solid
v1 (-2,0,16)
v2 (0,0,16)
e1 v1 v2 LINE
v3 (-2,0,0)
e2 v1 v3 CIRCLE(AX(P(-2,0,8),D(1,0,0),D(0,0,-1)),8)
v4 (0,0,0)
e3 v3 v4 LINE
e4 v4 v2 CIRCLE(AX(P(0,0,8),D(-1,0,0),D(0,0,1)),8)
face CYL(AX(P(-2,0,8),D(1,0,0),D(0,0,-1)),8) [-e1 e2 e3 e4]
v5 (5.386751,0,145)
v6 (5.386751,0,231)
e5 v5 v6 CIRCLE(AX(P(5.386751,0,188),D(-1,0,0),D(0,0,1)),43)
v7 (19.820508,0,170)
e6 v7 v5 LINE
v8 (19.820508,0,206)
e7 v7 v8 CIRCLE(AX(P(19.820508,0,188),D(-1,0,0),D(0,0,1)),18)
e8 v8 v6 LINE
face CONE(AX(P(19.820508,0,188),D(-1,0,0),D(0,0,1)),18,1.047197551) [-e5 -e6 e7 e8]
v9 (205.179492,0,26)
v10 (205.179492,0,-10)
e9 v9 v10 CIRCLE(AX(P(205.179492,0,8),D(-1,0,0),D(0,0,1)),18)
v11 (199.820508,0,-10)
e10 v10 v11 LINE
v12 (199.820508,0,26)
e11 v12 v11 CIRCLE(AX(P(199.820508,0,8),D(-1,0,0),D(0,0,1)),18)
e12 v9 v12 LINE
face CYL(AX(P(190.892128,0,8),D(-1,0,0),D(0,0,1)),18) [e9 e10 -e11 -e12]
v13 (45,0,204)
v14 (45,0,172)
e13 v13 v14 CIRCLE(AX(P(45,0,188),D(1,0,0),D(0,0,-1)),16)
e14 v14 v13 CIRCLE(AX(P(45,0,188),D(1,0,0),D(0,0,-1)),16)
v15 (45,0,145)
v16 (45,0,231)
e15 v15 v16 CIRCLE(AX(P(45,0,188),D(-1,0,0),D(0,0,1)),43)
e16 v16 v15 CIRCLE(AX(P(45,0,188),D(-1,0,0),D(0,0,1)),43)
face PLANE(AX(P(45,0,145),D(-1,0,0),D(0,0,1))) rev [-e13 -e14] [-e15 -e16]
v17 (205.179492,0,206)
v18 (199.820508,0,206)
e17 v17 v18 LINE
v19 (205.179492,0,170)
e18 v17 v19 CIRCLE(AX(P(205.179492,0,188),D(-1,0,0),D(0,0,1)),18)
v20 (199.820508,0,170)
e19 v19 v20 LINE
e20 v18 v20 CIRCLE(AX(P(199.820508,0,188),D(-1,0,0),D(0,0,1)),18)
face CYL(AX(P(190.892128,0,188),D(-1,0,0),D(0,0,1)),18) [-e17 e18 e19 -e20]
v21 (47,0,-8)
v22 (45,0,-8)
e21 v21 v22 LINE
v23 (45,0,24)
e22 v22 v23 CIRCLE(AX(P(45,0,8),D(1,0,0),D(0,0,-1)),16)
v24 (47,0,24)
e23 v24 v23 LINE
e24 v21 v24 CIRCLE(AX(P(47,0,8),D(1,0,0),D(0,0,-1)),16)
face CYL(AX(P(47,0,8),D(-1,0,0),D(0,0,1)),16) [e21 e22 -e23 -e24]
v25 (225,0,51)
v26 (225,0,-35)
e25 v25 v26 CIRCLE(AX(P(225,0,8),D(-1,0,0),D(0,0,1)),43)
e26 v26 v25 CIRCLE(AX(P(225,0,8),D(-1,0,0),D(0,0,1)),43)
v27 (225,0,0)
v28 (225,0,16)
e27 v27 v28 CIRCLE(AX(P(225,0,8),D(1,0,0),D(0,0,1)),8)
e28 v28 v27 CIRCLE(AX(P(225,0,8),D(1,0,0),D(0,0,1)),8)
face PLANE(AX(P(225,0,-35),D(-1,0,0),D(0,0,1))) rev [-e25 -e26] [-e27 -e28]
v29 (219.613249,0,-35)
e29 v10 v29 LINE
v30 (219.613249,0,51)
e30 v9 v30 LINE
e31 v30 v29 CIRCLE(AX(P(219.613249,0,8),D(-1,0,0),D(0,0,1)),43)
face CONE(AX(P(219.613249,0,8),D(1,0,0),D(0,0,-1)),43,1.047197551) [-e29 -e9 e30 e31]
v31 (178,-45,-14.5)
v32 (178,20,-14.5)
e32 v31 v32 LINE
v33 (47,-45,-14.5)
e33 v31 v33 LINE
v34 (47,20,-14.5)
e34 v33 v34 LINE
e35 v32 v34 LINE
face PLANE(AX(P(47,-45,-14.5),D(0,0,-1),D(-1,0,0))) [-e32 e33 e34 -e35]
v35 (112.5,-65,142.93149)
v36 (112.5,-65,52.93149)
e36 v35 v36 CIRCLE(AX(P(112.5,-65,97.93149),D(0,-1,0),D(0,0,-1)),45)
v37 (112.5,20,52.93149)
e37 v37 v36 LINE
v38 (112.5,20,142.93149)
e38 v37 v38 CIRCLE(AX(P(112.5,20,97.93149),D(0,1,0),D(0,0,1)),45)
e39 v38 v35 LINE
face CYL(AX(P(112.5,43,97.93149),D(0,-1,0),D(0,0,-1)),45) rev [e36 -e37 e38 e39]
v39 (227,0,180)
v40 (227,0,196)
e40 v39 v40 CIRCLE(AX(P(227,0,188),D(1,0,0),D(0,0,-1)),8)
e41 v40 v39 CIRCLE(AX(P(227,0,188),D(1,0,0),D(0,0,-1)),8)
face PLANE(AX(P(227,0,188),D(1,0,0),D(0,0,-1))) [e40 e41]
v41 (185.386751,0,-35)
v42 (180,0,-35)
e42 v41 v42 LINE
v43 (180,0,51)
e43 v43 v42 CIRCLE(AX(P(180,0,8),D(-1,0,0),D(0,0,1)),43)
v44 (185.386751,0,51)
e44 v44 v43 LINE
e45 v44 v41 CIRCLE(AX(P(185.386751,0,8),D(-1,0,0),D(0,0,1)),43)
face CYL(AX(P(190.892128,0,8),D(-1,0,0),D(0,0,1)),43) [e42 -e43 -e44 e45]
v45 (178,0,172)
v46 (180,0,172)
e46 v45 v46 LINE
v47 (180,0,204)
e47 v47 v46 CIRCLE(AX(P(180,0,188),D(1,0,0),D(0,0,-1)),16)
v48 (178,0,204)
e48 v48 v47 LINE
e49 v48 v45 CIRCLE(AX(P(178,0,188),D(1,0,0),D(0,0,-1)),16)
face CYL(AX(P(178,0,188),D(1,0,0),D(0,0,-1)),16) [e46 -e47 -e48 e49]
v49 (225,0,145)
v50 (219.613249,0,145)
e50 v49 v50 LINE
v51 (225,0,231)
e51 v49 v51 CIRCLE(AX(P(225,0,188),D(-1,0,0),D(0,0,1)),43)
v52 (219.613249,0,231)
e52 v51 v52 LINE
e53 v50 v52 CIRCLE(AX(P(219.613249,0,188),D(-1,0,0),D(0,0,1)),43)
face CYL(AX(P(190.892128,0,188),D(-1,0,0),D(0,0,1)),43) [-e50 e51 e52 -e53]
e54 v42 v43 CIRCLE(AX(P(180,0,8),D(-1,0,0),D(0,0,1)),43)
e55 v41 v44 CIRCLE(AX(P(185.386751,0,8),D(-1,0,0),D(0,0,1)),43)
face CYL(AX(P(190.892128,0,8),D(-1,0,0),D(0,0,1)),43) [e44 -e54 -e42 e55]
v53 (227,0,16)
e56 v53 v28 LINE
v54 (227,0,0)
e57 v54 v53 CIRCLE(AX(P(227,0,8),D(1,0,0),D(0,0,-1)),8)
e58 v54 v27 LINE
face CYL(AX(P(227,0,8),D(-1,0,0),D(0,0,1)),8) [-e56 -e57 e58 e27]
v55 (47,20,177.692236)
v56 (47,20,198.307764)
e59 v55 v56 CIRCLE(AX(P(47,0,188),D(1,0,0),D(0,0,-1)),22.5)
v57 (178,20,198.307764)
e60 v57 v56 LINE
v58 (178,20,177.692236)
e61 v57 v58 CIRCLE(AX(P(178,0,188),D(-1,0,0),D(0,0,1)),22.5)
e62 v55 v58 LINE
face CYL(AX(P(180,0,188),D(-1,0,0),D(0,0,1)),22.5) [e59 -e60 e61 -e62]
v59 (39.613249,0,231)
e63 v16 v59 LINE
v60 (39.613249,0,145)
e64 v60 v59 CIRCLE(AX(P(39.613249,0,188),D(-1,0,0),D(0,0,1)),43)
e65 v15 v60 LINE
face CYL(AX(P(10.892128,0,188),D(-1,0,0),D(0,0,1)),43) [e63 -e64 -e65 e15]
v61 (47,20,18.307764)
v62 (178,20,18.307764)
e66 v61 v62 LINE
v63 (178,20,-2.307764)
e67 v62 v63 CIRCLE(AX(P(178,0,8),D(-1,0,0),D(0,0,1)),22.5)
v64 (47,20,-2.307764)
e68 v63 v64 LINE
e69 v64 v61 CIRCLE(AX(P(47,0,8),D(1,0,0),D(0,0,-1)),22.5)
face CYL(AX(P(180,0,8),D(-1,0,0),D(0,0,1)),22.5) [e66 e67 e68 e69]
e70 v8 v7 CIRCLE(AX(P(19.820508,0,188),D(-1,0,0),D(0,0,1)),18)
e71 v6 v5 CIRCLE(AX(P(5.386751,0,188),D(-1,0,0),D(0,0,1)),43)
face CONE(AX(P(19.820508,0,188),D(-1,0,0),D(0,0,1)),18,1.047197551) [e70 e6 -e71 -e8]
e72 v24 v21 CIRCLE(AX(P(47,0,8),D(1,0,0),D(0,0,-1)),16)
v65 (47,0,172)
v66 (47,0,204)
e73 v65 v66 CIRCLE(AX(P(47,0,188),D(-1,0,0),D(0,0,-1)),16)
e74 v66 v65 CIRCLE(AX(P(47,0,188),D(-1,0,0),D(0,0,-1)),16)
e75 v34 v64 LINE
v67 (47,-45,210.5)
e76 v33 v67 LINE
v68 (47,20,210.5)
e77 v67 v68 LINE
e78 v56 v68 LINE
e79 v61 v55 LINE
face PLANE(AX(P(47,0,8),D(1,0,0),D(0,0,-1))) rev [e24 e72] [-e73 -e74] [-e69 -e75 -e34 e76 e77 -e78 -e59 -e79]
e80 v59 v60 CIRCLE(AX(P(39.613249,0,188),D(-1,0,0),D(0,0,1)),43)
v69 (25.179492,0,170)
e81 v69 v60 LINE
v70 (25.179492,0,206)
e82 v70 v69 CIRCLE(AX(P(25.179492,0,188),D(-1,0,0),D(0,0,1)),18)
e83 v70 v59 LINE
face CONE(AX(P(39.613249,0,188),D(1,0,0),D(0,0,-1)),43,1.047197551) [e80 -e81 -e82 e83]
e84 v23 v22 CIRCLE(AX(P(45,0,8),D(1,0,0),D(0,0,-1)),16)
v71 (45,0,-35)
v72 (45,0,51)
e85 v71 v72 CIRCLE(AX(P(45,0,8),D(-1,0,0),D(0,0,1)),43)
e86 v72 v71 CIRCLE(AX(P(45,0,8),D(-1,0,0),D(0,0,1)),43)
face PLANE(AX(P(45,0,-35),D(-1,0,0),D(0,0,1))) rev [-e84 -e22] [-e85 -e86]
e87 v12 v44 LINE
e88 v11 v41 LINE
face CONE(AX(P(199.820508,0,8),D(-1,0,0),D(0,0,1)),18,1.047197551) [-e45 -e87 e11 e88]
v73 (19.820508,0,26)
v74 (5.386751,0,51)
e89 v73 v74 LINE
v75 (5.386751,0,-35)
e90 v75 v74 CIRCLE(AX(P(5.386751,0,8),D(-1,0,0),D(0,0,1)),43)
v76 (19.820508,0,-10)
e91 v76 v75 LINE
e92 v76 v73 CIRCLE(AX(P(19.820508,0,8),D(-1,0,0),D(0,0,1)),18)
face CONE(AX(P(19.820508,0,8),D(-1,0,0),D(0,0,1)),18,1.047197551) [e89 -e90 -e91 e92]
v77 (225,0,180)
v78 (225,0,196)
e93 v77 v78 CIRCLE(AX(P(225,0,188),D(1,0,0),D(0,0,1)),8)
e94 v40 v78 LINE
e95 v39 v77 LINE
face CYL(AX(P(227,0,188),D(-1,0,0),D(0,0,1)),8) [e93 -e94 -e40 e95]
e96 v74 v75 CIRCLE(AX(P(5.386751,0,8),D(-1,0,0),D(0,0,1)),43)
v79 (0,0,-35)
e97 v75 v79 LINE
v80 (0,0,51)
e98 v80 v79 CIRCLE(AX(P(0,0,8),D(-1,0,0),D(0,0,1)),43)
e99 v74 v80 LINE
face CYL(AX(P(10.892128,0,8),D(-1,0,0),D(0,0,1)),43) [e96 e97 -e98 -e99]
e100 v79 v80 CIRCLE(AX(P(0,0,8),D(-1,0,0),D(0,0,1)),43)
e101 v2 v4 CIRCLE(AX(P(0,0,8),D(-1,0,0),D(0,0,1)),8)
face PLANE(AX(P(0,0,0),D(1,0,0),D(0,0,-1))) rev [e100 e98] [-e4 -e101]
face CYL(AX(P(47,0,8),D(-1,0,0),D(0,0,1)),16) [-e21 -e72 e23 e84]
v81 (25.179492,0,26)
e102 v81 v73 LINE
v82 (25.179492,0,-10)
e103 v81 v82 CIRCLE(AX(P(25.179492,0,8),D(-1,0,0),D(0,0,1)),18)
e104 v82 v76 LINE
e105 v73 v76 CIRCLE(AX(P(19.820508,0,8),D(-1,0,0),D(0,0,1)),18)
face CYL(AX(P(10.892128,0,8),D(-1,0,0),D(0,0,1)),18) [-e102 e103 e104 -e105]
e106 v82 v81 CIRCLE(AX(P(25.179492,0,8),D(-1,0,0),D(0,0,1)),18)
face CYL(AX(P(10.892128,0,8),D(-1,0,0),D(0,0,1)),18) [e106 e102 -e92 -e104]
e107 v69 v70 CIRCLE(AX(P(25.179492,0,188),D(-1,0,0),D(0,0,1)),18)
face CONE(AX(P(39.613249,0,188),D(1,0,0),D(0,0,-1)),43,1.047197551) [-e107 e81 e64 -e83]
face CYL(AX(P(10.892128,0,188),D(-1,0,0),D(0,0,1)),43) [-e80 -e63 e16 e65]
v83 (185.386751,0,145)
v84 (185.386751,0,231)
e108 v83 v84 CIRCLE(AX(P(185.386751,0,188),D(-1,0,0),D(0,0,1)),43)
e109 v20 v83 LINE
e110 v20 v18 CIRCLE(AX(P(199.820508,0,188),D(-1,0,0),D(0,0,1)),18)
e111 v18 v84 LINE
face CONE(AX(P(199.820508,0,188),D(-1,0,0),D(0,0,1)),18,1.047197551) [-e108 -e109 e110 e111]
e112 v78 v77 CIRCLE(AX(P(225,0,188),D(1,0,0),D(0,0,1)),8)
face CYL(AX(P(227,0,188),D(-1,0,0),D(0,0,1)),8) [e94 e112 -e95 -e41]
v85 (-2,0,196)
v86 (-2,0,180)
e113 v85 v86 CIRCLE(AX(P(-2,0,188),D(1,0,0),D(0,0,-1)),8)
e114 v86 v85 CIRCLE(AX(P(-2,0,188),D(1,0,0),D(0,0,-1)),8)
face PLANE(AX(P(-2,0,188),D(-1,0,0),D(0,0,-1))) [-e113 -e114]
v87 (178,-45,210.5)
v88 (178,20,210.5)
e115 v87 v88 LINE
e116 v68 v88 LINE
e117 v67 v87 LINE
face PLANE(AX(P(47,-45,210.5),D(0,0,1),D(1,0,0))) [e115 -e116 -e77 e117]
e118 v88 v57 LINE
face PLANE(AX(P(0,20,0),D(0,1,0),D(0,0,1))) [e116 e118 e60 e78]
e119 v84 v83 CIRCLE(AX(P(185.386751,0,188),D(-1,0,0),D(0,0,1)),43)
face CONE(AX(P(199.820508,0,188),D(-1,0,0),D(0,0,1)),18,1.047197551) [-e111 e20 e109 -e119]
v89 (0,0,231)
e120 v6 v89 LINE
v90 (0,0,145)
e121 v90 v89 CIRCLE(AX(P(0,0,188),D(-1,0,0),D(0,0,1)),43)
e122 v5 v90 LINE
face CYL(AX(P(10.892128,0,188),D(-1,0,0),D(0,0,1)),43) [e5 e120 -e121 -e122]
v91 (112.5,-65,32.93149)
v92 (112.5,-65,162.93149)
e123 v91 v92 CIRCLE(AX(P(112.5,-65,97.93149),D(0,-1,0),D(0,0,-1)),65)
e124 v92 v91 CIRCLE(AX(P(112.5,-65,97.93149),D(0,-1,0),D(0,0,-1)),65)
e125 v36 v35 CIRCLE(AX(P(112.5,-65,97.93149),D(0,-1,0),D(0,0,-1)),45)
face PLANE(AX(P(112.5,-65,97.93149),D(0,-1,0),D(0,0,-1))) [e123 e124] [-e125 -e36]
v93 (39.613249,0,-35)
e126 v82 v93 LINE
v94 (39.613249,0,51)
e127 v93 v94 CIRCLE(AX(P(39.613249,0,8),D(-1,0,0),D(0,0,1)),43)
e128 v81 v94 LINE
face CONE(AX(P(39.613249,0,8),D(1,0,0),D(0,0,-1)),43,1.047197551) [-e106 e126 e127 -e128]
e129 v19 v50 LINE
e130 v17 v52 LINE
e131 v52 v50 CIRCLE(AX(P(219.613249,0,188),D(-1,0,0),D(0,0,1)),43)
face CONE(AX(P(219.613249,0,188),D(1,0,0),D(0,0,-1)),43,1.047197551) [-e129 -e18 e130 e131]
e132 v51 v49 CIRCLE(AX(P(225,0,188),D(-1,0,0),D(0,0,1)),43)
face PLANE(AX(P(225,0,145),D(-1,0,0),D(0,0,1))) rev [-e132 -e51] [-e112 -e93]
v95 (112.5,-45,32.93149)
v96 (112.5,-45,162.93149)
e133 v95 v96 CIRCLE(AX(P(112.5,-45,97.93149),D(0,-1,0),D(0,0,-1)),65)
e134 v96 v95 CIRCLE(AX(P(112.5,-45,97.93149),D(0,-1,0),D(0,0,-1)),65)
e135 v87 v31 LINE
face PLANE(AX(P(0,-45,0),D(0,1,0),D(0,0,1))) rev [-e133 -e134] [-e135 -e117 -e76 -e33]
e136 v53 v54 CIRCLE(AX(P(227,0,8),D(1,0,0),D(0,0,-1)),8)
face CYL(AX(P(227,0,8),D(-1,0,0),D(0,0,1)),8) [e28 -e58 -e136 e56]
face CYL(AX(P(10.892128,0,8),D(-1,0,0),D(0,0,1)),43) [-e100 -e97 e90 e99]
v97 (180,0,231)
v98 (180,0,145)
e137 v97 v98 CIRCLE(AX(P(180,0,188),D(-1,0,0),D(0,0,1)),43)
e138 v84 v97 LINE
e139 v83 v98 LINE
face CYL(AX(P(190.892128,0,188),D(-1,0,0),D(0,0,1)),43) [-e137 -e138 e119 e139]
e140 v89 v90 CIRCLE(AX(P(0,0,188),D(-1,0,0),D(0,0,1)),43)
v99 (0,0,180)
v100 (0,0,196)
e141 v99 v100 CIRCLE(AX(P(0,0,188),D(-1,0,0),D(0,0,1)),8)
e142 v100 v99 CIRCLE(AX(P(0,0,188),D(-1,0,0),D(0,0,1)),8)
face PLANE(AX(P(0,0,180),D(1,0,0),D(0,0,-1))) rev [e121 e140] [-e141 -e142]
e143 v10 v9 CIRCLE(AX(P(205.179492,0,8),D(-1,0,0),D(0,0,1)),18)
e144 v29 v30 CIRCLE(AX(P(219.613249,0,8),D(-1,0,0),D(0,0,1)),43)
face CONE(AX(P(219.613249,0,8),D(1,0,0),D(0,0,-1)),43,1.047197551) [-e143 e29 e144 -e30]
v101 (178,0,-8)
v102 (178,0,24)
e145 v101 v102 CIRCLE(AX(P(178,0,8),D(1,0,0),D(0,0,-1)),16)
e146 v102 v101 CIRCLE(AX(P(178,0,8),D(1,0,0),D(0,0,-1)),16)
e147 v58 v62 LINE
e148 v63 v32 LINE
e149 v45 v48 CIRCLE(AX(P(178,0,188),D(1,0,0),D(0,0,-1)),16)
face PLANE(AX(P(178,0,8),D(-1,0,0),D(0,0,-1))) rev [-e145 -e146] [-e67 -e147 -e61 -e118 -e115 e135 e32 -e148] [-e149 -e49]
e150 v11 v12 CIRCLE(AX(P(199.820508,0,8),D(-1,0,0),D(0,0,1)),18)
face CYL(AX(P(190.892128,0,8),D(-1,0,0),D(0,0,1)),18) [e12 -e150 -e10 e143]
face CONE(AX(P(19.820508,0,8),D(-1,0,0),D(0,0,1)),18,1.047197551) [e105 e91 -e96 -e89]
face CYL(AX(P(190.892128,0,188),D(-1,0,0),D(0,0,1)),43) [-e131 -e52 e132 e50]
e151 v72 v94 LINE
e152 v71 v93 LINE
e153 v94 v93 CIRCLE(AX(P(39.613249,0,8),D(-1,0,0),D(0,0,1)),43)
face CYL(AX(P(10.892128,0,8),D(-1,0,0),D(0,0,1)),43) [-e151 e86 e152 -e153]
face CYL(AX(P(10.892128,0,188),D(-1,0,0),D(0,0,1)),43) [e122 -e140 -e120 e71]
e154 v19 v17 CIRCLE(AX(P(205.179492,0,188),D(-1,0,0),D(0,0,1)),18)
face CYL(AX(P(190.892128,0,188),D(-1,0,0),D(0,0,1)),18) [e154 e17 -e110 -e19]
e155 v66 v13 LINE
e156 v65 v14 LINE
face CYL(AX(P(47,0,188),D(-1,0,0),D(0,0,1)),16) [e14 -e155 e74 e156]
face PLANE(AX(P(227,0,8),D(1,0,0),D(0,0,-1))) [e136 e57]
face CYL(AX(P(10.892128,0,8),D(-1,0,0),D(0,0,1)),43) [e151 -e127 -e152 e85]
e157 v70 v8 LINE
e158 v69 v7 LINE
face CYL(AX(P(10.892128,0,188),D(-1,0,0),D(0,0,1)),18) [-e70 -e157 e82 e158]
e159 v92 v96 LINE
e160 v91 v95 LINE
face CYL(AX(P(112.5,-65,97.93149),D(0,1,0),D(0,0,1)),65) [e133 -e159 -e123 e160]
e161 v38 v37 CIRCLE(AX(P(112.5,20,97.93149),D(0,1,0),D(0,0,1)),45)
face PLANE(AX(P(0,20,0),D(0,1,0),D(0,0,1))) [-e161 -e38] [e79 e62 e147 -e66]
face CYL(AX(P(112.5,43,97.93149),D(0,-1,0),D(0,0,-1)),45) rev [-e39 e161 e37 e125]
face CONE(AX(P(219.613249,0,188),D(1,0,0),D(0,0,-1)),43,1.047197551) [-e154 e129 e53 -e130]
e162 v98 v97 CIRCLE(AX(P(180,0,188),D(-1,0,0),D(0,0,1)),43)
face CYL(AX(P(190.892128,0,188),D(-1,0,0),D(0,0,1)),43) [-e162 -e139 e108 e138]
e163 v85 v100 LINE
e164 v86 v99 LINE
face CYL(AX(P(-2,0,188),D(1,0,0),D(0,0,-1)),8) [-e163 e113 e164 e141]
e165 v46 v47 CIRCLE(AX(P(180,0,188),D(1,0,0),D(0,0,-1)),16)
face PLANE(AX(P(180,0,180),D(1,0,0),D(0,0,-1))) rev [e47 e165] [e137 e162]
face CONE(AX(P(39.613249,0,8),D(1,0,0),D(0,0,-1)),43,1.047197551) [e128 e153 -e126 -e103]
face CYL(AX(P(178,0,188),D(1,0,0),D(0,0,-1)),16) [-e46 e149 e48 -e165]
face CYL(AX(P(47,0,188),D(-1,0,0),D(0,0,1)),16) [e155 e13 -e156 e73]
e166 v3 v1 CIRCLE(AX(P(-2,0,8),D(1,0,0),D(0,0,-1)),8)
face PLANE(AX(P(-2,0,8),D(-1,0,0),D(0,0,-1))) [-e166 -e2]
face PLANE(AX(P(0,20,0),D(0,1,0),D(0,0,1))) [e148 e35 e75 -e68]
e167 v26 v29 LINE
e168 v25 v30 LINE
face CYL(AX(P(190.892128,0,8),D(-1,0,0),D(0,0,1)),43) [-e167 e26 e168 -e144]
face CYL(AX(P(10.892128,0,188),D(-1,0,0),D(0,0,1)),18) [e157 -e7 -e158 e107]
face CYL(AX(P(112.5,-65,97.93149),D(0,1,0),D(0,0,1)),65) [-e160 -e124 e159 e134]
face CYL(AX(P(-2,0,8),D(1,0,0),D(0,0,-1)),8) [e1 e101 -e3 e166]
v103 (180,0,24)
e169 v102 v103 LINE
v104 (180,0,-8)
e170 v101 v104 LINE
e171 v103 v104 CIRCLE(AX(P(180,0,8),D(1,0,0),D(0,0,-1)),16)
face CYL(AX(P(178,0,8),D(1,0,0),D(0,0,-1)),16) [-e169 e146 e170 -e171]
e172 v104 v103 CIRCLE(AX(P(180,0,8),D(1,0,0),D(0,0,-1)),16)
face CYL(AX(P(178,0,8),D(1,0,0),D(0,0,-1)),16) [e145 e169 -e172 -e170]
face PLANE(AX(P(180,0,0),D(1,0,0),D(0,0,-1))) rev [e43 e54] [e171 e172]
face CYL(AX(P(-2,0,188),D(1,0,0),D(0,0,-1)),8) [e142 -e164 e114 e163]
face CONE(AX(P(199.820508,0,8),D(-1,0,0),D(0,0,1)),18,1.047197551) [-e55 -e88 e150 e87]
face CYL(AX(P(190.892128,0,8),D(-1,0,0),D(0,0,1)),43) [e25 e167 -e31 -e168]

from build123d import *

# Parameters (mm, degrees)
LPATTERN1_COUNT          = 2
LPATTERN1_PITCH          = 180
SKETCH3_R                = 22.5
BOSS_EXTRUDE2_DEPTH      = 135
SKETCH4_R                = 30.412434653
SKETCH4_R_2              = 16
CUT_EXTRUDE1_DEPTH       = 2
SKETCH5_R                = 8
BOSS_EXTRUDE3_DEPTH      = 47
LPATTERN2_COUNT          = 2
LPATTERN2_PITCH          = 180
BOSS_EXTRUDE4_DEPTH      = 20
BOSS_EXTRUDE4_DEPTH_BACK = 45
SKETCH6_W                = 131
SKETCH6_H                = 225
SKETCH7_R                = 65
BOSS_EXTRUDE5_DEPTH      = 20
CUT_EXTRUDE2_DEPTH       = 342.400058582
CUT_EXTRUDE2_DEPTH_BACK  = 342.400058582
SKETCH8_R                = 45


with BuildPart() as part:
    # Sketch2 → Revolve1 (revolve)
    with BuildSketch(Plane(origin=(0, 0, 0), x_dir=(1, 0, 0), z_dir=(0, 1, 0)), mode=Mode.PRIVATE) as revolve1_sk:
        Polygon((0, 0), (0, 35), (5.386751346, 35), (19.820508076, 10), (25.179491924, 10), (39.613248654, 35), (45, 35), (45, 0), align=None)
    revolve(revolve1_sk.sketch.rotate(Axis((10.892128266, 0, 8), (1, 0, 0)), 180), axis=Axis((10.892128266, 0, 8), (1, 0, 0)))


with BuildPart() as lpattern1_1:
    # LPattern1: pattern copy
    add(part.part.moved(Location(Vector(1, 0, 0) * (1 * LPATTERN1_PITCH))))


with BuildPart() as part_1:
    add(part.part)

    add(lpattern1_1.part)  # Boss-Extrude2 merges LPattern1_1
    # Sketch3 → Boss-Extrude2 (add)
    with BuildSketch(Plane(origin=(45, 0, 0), x_dir=(0, 0, -1), z_dir=(1, 0, 0))):
        with Locations(Location((-8, 0, 0), (0, 0, 180))):
            Circle(SKETCH3_R)
    extrude(amount=BOSS_EXTRUDE2_DEPTH)

    # Sketch4 → Cut-Extrude1 (cut)
    with BuildSketch(Plane(origin=(45, 0, 0), x_dir=(0, 0, -1), z_dir=(1, 0, 0))):
        with Locations((-8, 0)):
            Circle(SKETCH4_R)
        with Locations((-8, 0)):
            Circle(SKETCH4_R_2, mode=Mode.SUBTRACT)
    cut_extrude1 = extrude(amount=CUT_EXTRUDE1_DEPTH, mode=Mode.SUBTRACT)

    # Mirror1: Cut-Extrude1 across plane
    add(cut_extrude1.mirror(Plane.ZY.offset(-112.5)), mode=Mode.SUBTRACT)

    # Sketch5 → Boss-Extrude3 (add)
    with BuildSketch(Plane(origin=(180, 0, 0), x_dir=(0, 0, -1), z_dir=(1, 0, 0))):
        with Locations(Location((-8, 0, 0), (0, 0, 180))):
            Circle(SKETCH5_R)
    boss_extrude3 = extrude(amount=BOSS_EXTRUDE3_DEPTH)

    # Mirror2: Boss-Extrude3 across plane
    add(boss_extrude3.mirror(Plane.ZY.offset(-112.5)))


with BuildPart() as lpattern2_1:
    # LPattern2: pattern copy
    add(part_1.part.moved(Location(Vector(0, 0, 1) * (1 * LPATTERN2_PITCH))))


with BuildPart() as part_2:
    add(part_1.part)

    add(lpattern2_1.part)  # Boss-Extrude4 merges LPattern2_1
    # Sketch6 → Boss-Extrude4 (add, two sides: drawn at the far end of the back side and taken through both)
    with BuildSketch(Plane(origin=(0, 0, 0), x_dir=(1, 0, 0), z_dir=(0, 1, 0)).offset(-BOSS_EXTRUDE4_DEPTH_BACK)):
        with Locations((112.5, -98)):
            Rectangle(SKETCH6_W, SKETCH6_H)
    extrude(amount=BOSS_EXTRUDE4_DEPTH + BOSS_EXTRUDE4_DEPTH_BACK)

    # Sketch7 → Boss-Extrude5 (add)
    with BuildSketch(Plane.XZ.offset(45)):
        with Locations(Location((112.5, 97.931490015, 0), (0, 0, 270))):
            Circle(SKETCH7_R)
    extrude(amount=BOSS_EXTRUDE5_DEPTH)

    # Sketch8 → Cut-Extrude2 (cut, two sides: drawn at the far end of the back side and taken through both)
    with BuildSketch(Plane.XZ.offset(65).offset(-CUT_EXTRUDE2_DEPTH_BACK)):
        with Locations(Location((112.5, 97.931490015, 0), (0, 0, 270))):
            Circle(SKETCH8_R)
    extrude(amount=CUT_EXTRUDE2_DEPTH + CUT_EXTRUDE2_DEPTH_BACK, mode=Mode.SUBTRACT)


solid = part_2.part
